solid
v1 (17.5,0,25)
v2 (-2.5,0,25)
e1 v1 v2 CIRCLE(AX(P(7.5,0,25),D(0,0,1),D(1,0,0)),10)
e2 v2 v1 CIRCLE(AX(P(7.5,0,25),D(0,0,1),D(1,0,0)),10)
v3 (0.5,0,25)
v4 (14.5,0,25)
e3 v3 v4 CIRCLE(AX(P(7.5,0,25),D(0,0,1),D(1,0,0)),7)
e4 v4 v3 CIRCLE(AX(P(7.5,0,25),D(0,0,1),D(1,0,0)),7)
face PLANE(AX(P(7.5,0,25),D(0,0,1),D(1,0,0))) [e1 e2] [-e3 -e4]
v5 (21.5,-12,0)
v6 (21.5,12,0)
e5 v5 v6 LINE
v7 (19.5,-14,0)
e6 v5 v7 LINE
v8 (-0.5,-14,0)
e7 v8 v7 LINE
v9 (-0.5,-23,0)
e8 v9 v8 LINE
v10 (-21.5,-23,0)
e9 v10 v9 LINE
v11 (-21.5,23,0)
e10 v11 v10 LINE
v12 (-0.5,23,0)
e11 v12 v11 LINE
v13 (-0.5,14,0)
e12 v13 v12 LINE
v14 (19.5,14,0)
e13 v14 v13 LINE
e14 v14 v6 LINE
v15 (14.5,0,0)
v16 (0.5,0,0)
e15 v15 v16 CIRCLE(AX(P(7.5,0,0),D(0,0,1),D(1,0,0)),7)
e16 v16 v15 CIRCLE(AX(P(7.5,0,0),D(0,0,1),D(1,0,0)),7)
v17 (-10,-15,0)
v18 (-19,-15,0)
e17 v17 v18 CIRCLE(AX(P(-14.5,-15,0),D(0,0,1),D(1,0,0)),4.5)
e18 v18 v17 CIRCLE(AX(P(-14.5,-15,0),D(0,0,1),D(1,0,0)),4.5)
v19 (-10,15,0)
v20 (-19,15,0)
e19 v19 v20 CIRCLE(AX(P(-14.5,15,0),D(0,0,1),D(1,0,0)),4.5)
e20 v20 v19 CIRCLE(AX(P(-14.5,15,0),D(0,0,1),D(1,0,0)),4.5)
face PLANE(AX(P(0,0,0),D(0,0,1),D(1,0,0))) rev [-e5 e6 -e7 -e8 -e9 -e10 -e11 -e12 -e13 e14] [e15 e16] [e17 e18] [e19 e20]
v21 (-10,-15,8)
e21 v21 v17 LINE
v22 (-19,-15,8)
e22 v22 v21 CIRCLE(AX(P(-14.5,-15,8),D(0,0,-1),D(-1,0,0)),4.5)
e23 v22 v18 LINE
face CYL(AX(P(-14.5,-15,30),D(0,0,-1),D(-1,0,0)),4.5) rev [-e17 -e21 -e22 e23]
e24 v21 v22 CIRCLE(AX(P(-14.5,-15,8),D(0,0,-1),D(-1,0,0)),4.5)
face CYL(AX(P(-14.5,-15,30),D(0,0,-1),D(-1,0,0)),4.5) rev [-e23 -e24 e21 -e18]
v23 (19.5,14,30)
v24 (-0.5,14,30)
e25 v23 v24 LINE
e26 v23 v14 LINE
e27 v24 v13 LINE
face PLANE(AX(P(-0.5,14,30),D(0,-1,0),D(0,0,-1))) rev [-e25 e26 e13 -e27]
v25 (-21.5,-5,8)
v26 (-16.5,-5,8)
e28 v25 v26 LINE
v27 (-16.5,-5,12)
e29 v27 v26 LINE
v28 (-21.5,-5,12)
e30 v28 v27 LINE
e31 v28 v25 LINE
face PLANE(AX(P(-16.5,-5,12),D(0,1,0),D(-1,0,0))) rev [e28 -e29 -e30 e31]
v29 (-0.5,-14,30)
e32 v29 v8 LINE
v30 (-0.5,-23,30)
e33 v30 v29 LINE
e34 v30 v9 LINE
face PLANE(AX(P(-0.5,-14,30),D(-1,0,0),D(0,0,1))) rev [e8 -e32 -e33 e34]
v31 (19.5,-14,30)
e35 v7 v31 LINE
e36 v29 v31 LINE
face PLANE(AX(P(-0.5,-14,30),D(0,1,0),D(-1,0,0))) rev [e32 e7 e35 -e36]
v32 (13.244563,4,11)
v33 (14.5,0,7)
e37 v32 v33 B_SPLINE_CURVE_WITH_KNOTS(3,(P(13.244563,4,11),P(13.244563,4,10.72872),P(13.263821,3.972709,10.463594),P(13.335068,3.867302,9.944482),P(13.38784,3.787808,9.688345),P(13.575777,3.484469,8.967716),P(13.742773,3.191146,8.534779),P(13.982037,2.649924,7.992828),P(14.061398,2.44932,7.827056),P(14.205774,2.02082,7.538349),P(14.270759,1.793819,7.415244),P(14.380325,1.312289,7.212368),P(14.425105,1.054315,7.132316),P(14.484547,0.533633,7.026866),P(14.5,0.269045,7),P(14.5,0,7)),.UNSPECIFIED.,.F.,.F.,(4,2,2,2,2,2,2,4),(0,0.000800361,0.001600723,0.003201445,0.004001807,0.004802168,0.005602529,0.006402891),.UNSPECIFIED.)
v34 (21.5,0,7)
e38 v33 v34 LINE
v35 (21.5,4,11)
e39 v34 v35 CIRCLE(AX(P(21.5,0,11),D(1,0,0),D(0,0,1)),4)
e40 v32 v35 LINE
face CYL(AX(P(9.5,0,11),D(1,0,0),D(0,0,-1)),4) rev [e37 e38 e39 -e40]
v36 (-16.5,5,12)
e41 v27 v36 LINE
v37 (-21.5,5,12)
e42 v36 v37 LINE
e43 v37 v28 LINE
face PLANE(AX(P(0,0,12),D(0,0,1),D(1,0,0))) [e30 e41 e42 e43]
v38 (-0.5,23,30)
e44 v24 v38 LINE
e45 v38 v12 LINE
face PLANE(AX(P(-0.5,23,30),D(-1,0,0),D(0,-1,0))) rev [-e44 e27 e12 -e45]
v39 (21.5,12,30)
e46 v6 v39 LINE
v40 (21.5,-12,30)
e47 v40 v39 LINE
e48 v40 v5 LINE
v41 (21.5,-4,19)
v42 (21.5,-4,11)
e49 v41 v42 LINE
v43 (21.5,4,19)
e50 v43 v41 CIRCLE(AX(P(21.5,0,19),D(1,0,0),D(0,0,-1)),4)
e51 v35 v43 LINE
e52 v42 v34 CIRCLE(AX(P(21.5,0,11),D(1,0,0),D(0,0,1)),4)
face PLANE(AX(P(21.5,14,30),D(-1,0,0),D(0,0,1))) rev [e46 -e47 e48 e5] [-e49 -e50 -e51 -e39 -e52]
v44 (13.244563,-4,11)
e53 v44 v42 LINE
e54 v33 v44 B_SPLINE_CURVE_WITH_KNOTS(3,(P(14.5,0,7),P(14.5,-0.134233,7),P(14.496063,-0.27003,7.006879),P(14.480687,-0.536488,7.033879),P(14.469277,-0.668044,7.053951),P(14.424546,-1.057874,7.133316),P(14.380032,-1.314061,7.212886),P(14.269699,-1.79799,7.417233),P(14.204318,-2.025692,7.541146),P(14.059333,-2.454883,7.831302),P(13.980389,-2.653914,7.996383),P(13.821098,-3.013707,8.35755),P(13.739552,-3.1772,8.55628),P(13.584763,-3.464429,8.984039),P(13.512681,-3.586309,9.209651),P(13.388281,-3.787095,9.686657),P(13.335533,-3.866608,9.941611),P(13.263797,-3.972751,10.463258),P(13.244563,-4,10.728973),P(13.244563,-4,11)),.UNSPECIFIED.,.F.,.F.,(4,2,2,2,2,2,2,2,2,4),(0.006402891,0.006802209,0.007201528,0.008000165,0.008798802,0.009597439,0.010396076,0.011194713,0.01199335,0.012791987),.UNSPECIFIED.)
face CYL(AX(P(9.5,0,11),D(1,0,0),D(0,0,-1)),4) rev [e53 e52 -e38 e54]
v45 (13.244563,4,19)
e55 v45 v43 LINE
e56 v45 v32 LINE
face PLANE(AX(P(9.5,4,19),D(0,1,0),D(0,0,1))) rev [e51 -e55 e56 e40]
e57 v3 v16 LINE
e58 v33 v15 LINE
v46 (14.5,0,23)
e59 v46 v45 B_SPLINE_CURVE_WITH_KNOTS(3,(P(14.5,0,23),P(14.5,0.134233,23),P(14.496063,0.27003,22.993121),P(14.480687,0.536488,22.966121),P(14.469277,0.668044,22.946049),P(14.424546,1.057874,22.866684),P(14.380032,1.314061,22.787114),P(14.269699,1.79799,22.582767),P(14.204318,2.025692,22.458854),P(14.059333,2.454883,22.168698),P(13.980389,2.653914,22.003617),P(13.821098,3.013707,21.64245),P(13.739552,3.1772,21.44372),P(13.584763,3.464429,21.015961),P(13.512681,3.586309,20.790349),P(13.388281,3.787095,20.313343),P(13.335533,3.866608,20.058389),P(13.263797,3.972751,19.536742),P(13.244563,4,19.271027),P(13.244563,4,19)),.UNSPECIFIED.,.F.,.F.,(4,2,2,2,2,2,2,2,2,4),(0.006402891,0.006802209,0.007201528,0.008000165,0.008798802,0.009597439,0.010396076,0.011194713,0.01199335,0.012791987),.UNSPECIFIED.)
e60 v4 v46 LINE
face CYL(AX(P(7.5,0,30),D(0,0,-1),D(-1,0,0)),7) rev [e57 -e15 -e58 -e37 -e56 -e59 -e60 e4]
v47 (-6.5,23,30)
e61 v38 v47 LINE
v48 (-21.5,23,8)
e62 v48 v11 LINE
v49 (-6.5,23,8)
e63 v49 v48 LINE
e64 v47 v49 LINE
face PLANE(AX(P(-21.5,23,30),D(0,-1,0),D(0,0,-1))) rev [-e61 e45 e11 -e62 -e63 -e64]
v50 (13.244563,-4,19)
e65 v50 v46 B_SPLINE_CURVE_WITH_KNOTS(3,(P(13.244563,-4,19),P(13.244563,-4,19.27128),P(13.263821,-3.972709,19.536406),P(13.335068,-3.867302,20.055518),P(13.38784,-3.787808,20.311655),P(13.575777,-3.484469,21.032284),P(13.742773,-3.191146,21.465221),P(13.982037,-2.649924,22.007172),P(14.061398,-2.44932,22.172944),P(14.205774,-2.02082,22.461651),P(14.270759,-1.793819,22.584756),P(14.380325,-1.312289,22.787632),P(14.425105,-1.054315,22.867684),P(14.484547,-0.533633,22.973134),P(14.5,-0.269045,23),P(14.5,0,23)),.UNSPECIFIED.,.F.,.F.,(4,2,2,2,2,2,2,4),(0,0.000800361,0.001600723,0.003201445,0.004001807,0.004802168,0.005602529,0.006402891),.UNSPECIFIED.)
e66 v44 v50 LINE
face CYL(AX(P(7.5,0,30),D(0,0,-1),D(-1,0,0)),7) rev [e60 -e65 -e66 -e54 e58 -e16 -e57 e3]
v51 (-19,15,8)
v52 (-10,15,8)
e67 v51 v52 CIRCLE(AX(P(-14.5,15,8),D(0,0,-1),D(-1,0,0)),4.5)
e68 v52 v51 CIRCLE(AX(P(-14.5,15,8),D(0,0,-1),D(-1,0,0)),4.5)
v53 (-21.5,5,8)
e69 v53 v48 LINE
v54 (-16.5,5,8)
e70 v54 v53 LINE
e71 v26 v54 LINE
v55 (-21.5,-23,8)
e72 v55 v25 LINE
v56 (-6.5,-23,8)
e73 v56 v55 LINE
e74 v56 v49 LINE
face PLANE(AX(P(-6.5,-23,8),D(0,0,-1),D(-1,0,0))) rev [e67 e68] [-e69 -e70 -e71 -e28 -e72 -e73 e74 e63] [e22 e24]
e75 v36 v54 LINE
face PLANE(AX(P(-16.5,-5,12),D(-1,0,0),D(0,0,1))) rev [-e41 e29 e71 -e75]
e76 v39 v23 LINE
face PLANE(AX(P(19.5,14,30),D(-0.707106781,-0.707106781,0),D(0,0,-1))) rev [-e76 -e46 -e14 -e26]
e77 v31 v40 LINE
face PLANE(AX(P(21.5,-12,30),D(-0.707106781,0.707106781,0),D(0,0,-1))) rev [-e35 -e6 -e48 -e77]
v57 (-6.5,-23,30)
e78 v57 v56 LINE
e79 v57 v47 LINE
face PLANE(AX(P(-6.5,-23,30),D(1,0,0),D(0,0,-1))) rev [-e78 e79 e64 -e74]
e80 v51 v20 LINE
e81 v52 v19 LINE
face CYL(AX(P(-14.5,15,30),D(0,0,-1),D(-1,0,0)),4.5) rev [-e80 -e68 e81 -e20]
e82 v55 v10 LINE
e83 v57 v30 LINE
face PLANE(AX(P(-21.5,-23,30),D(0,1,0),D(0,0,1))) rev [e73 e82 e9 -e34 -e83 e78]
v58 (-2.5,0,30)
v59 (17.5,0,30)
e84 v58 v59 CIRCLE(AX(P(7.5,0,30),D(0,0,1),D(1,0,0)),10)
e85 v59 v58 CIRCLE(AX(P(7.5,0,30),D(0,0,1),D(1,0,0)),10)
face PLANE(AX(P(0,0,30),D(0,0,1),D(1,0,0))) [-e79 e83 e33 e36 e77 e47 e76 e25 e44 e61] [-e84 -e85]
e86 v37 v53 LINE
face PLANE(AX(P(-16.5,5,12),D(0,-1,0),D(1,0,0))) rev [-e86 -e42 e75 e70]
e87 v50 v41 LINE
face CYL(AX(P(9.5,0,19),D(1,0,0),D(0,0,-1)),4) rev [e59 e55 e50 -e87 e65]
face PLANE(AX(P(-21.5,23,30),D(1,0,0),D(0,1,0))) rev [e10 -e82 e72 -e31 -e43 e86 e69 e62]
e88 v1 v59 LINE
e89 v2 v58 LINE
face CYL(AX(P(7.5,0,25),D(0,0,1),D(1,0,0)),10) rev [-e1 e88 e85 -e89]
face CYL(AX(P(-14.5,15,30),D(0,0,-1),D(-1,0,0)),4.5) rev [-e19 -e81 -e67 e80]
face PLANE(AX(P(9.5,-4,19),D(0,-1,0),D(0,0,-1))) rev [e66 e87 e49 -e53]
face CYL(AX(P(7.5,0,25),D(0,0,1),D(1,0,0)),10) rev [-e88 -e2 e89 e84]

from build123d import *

# Parameters (mm, degrees)
SKETCH1_R           = 7
SKETCH1_R_2         = 4.5
BOSS_EXTRUDE1_DEPTH = 30
SKETCH2_W           = 15
SKETCH2_H           = 22
CUT_EXTRUDE1_DEPTH  = 59.976690311
CHAMFER1_SIZE       = 2
SKETCH3_R           = 10
CUT_EXTRUDE2_DEPTH  = 5
SKETCH4_W           = 5
SKETCH4_H           = 10
BOSS_EXTRUDE2_DEPTH = 4
CUT_EXTRUDE3_DEPTH  = 12


with BuildPart() as part:
    # Sketch1 → Boss-Extrude1 (new body)
    with BuildSketch(Plane.XY):
        Polygon((-21.5, 23), (-0.5, 23), (-0.5, 14), (21.5, 14), (21.5, -14), (-0.5, -14), (-0.5, -23), (-21.5, -23), align=None)
        with Locations((7.5, 0)):
            Circle(SKETCH1_R, mode=Mode.SUBTRACT)
        with Locations((-14.5, 15)):
            Circle(SKETCH1_R_2, mode=Mode.SUBTRACT)
        with Locations((-14.5, -15)):
            Circle(SKETCH1_R_2, mode=Mode.SUBTRACT)
    extrude(amount=BOSS_EXTRUDE1_DEPTH)

    # Sketch2 → Cut-Extrude1 (cut, through all)
    with BuildSketch(Plane(origin=(0, 23, 0), x_dir=(1, 0, 0), z_dir=(0, 1, 0))):
        with Locations((-14, -19)):
            Rectangle(SKETCH2_W, SKETCH2_H)
    extrude(amount=-CUT_EXTRUDE1_DEPTH, mode=Mode.SUBTRACT)

    # Chamfer1
    chamfer1_edges = [part.edges().sort_by_distance(p)[0] for p in [
        (21.5, 14, 15),
        (21.5, -14, 15),
    ]]
    chamfer(chamfer1_edges, length=CHAMFER1_SIZE)

    # Sketch3 → Cut-Extrude2 (cut)
    with BuildSketch(Plane.XY.offset(30)):
        with Locations((7.5, 0)):
            Circle(SKETCH3_R)
    extrude(amount=-CUT_EXTRUDE2_DEPTH, mode=Mode.SUBTRACT)

    # Sketch4 → Boss-Extrude2 (add)
    with BuildSketch(Plane.XY.offset(8)):
        with Locations((-19, 0)):
            Rectangle(SKETCH4_W, SKETCH4_H)
    extrude(amount=BOSS_EXTRUDE2_DEPTH)

    # Sketch5 → Cut-Extrude3 (cut)
    with BuildSketch(Plane(origin=(21.5, 0, 0), x_dir=(0, 0, -1), z_dir=(1, 0, 0))):
        with BuildLine():
            Line((-19, 4), (-11, 4))
            ThreePointArc((-11, 4), (-7, 0), (-11, -4))
            Line((-11, -4), (-19, -4))
            ThreePointArc((-19, -4), (-23, 0), (-19, 4))
        make_face()
    extrude(amount=-CUT_EXTRUDE3_DEPTH, mode=Mode.SUBTRACT)


solid = part.part
